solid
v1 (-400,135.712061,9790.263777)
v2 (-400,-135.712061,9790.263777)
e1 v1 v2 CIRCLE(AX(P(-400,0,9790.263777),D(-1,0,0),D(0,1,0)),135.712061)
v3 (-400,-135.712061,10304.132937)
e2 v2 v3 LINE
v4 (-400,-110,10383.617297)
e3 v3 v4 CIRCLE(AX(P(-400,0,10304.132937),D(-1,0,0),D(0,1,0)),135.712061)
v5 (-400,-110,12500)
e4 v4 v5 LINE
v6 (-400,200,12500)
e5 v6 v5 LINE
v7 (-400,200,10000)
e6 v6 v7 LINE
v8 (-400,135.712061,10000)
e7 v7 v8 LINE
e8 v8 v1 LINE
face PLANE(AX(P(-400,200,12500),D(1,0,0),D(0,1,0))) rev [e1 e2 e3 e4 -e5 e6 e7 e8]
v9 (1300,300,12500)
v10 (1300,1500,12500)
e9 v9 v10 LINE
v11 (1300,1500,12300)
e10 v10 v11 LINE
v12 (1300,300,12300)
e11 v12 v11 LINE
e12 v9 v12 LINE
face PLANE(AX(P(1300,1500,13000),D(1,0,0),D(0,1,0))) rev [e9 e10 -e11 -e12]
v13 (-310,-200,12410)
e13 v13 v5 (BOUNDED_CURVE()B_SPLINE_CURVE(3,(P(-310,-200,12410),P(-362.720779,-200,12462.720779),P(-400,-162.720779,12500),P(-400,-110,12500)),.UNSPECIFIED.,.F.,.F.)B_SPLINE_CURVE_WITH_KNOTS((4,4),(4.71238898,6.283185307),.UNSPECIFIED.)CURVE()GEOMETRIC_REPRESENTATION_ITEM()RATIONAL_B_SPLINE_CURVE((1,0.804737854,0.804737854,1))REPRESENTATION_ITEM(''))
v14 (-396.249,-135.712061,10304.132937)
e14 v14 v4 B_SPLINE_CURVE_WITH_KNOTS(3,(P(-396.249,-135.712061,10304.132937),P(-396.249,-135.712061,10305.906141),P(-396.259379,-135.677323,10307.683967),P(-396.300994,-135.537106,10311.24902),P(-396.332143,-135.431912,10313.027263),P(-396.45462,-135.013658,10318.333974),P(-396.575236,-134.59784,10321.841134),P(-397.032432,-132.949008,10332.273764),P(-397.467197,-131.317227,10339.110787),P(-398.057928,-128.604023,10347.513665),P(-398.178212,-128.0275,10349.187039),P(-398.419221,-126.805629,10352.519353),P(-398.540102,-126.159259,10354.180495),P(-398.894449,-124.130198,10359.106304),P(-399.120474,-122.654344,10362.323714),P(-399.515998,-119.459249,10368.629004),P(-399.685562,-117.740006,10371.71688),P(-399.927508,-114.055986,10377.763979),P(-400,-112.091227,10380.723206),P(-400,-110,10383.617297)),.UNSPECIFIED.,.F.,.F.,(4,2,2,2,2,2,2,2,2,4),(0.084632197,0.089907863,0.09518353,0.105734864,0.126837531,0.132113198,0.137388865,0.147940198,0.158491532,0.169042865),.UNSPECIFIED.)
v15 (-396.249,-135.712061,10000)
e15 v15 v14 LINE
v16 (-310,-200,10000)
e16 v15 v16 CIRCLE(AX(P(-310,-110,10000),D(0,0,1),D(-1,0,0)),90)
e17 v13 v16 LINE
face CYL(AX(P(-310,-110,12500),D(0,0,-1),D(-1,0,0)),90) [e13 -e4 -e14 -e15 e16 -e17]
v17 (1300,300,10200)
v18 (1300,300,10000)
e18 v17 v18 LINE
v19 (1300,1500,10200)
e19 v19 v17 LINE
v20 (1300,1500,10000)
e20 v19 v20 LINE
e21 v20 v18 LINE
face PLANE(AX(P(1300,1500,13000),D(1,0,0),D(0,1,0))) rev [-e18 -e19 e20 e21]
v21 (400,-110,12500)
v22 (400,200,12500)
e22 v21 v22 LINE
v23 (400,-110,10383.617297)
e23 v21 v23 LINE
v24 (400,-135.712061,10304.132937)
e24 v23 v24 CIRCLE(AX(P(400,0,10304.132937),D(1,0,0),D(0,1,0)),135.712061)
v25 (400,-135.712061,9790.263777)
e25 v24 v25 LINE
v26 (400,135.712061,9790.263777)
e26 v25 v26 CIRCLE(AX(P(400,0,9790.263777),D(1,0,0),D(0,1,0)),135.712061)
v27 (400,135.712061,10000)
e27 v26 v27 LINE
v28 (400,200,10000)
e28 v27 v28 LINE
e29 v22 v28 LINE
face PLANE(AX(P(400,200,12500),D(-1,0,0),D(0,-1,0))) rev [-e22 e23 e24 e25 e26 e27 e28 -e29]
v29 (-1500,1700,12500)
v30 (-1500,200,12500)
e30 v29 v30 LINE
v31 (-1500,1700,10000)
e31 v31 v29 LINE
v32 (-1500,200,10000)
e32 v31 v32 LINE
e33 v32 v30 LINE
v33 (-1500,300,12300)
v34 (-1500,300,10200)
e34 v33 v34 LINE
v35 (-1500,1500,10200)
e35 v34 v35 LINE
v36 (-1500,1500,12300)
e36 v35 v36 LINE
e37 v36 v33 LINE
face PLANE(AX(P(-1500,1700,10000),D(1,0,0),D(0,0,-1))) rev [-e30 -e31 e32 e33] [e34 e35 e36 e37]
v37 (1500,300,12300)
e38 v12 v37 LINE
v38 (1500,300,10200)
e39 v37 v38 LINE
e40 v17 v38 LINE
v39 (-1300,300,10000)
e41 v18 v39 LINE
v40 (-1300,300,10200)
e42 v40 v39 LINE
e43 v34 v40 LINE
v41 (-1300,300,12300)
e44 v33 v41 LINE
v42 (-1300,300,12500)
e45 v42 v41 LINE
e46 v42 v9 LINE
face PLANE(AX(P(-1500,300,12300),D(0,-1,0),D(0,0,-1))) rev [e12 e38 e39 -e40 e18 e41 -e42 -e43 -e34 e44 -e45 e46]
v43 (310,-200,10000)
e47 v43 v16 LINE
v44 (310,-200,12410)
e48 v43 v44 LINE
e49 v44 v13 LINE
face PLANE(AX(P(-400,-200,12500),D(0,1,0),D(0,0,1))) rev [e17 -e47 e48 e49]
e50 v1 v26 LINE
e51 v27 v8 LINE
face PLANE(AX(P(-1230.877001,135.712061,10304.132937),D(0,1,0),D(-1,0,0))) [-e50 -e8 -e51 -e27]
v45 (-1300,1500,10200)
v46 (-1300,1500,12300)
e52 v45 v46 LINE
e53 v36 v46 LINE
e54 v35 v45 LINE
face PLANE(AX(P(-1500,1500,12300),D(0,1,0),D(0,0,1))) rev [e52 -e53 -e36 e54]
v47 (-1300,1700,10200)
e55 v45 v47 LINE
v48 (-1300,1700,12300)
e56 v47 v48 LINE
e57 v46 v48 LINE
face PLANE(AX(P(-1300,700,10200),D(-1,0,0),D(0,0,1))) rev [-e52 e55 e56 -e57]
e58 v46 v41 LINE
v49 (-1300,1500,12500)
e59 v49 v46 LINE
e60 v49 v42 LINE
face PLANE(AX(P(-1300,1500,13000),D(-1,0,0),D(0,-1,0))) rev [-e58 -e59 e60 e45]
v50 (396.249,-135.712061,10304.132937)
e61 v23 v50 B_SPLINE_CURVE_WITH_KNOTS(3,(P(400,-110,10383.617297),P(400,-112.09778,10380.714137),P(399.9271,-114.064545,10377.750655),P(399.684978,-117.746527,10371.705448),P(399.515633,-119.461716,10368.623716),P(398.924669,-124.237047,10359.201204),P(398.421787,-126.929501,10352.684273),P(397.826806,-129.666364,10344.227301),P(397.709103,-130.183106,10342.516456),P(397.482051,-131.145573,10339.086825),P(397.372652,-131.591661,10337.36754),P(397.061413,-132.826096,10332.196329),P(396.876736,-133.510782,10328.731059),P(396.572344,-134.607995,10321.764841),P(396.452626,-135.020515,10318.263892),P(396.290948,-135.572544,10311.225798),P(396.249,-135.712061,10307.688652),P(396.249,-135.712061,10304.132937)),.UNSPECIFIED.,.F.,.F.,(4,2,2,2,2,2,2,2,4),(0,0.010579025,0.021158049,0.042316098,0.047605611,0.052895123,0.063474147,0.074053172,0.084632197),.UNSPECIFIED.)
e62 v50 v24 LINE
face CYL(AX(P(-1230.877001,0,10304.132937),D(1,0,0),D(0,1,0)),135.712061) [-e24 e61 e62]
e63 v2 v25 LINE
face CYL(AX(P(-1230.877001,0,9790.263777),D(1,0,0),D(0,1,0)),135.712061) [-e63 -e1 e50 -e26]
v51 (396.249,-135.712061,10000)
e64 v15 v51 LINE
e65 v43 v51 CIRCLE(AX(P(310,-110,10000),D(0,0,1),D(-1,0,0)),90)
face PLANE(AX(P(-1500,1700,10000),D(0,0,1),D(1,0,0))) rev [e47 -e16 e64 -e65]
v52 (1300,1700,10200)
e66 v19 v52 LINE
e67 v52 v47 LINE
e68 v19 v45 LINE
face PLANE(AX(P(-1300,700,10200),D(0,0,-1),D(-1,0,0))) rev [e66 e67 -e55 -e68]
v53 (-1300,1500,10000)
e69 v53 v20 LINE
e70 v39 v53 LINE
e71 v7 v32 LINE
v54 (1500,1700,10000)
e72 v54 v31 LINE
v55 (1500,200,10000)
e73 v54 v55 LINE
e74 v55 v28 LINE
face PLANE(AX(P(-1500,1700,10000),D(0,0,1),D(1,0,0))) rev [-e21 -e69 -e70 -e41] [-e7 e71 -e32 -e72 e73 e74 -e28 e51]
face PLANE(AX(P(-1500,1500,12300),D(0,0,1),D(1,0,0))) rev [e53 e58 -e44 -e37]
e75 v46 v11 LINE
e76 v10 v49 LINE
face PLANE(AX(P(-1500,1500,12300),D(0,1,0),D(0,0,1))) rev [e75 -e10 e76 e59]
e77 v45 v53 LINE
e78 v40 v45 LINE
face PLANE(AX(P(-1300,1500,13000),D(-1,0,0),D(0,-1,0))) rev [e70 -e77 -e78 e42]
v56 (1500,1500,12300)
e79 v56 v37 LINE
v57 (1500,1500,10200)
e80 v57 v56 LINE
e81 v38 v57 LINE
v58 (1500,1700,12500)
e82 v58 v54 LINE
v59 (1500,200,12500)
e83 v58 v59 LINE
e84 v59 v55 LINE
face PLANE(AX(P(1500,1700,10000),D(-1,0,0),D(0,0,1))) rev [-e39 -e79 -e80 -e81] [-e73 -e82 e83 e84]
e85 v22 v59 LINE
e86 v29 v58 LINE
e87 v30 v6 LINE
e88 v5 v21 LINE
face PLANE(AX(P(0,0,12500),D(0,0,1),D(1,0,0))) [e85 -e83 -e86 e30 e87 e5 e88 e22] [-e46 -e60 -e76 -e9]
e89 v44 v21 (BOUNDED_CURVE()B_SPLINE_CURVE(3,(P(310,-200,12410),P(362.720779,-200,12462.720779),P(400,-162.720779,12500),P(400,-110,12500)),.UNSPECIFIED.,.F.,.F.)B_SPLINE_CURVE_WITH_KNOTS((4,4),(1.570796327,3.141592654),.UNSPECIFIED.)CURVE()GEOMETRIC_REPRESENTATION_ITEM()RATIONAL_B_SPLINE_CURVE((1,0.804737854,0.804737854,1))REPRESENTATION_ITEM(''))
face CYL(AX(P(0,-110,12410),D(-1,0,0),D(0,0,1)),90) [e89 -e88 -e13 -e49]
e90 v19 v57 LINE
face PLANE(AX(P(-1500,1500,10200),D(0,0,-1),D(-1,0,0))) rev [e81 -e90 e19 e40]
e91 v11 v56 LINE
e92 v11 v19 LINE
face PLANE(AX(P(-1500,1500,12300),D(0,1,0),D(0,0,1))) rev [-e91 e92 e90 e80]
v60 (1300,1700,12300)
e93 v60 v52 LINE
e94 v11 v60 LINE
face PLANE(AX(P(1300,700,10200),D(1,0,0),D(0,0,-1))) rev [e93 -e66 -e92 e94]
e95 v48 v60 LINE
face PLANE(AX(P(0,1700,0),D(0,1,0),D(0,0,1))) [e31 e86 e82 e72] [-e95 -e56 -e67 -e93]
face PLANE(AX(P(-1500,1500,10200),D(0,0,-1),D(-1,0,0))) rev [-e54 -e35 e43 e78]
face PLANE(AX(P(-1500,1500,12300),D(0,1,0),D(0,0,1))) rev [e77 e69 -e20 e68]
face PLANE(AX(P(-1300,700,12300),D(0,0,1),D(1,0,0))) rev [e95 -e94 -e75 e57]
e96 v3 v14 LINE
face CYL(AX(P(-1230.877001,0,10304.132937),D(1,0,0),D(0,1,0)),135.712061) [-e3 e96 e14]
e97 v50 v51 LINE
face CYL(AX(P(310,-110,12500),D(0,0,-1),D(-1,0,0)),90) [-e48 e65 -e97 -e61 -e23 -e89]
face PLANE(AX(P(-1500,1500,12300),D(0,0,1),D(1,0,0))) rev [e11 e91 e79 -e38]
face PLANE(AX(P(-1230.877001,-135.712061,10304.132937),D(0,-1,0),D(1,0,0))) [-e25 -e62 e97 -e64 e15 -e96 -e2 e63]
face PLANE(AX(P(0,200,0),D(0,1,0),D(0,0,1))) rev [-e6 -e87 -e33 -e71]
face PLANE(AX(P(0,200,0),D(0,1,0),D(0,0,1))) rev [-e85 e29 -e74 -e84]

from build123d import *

# Parameters (mm, degrees)
SKETCH1_W           = 800
SKETCH1_H           = 400
BOSS_EXTRUDE1_DEPTH = 12500
SKETCH2_W           = 3000
SKETCH2_H           = 2500
BOSS_EXTRUDE2_DEPTH = 1500
SKETCH3_W           = 2100
SKETCH3_H           = 1200
CUT_EXTRUDE1_DEPTH  = 3000
SKETCH4_W           = 2600
SKETCH4_H           = 1200
CUT_EXTRUDE2_DEPTH  = 3000
SKETCH5_W           = 2600
SKETCH5_H           = 2100
CUT_EXTRUDE3_DEPTH  = 1000
FILLET1_R           = 90
SKETCH6_W           = 1631.27980794
SKETCH6_H           = 982.131348286
CUT_EXTRUDE4_DEPTH  = 10254.779790887
BOSS_EXTRUDE3_REACH = 12759.351


with BuildPart() as part:
    # Sketch1 → Boss-Extrude1 (new body)
    with BuildSketch(Plane.XY):
        Rectangle(SKETCH1_W, SKETCH1_H)
    extrude(amount=BOSS_EXTRUDE1_DEPTH)

    # Sketch2 → Boss-Extrude2 (add)
    with BuildSketch(Plane(origin=(0, 200, 0), x_dir=(1, 0, 0), z_dir=(0, 1, 0))):
        with Locations((0, -11250)):
            Rectangle(SKETCH2_W, SKETCH2_H)
    extrude(amount=BOSS_EXTRUDE2_DEPTH)

    # Sketch3 → Cut-Extrude1 (cut)
    with BuildSketch(Plane(origin=(1500, 0, 0), x_dir=(0, 0, -1), z_dir=(1, 0, 0))):
        with Locations((-11250, 900)):
            Rectangle(SKETCH3_W, SKETCH3_H)
    extrude(amount=-CUT_EXTRUDE1_DEPTH, mode=Mode.SUBTRACT)

    # Sketch4 → Cut-Extrude2 (cut)
    with BuildSketch(Plane(origin=(0, 0, 10000), x_dir=(-1, 0, 0), z_dir=(0, 0, -1))):
        with Locations((0, 900)):
            Rectangle(SKETCH4_W, SKETCH4_H)
    extrude(amount=-CUT_EXTRUDE2_DEPTH, mode=Mode.SUBTRACT)

    # Sketch5 → Cut-Extrude3 (cut)
    with BuildSketch(Plane(origin=(0, 1700, 0), x_dir=(1, 0, 0), z_dir=(0, 1, 0))):
        with Locations((0, -11250)):
            Rectangle(SKETCH5_W, SKETCH5_H)
    extrude(amount=-CUT_EXTRUDE3_DEPTH, mode=Mode.SUBTRACT)

    # Fillet1
    fillet1_edges = [part.edges().sort_by_distance(p)[0] for p in [
        (-400, 200, 5000),
        (400, 200, 5000),
        (0, -200, 12500),
        (400, -200, 6250),
        (-400, -200, 6250),
    ]]
    fillet(fillet1_edges, radius=FILLET1_R)

    # Sketch6 → Cut-Extrude4 (cut, through all)
    with BuildSketch(Plane(origin=(0, 0, 10000), x_dir=(-1, 0, 0), z_dir=(0, 0, -1))):
        with Locations((-94.176978603, 201.755445991)):
            Rectangle(SKETCH6_W, SKETCH6_H)
    extrude(amount=CUT_EXTRUDE4_DEPTH, mode=Mode.SUBTRACT)

    # Boss-Extrude3: up to this face of the body (flat: up to its plane)
    boss_extrude3_end = Plane(part.part.faces().sort_by_distance((-400, 45, 11250))[0])
    # Sketch7 → Boss-Extrude3 (add, up to the picked face)
    with BuildSketch(Plane(origin=(400, 0, 0), x_dir=(0, 0, -1), z_dir=(1, 0, 0)), mode=Mode.PRIVATE) as boss_extrude3_sk1:
        with BuildLine():
            Line((-10304.132937167, 135.712060669), (-9790.263777043, 135.712060669))
            ThreePointArc((-9790.263777043, 135.712060669), (-9654.551716374, 0), (-9790.263777043, -135.712060669))
            Line((-9790.263777043, -135.712060669), (-10304.132937167, -135.712060669))
            ThreePointArc((-10304.132937167, -135.712060669), (-10439.844997836, 0), (-10304.132937167, 135.712060669))
        make_face()
    boss_extrude3_tool1 = split(extrude(boss_extrude3_sk1.sketch, amount=-BOSS_EXTRUDE3_REACH, mode=Mode.PRIVATE), bisect_by=boss_extrude3_end, keep=Keep.BOTH, mode=Mode.PRIVATE)
    add(boss_extrude3_tool1.solids().sort_by(Axis((400, 0, 10047.198357), (-1, 0, 0)))[0])


solid = part.part
